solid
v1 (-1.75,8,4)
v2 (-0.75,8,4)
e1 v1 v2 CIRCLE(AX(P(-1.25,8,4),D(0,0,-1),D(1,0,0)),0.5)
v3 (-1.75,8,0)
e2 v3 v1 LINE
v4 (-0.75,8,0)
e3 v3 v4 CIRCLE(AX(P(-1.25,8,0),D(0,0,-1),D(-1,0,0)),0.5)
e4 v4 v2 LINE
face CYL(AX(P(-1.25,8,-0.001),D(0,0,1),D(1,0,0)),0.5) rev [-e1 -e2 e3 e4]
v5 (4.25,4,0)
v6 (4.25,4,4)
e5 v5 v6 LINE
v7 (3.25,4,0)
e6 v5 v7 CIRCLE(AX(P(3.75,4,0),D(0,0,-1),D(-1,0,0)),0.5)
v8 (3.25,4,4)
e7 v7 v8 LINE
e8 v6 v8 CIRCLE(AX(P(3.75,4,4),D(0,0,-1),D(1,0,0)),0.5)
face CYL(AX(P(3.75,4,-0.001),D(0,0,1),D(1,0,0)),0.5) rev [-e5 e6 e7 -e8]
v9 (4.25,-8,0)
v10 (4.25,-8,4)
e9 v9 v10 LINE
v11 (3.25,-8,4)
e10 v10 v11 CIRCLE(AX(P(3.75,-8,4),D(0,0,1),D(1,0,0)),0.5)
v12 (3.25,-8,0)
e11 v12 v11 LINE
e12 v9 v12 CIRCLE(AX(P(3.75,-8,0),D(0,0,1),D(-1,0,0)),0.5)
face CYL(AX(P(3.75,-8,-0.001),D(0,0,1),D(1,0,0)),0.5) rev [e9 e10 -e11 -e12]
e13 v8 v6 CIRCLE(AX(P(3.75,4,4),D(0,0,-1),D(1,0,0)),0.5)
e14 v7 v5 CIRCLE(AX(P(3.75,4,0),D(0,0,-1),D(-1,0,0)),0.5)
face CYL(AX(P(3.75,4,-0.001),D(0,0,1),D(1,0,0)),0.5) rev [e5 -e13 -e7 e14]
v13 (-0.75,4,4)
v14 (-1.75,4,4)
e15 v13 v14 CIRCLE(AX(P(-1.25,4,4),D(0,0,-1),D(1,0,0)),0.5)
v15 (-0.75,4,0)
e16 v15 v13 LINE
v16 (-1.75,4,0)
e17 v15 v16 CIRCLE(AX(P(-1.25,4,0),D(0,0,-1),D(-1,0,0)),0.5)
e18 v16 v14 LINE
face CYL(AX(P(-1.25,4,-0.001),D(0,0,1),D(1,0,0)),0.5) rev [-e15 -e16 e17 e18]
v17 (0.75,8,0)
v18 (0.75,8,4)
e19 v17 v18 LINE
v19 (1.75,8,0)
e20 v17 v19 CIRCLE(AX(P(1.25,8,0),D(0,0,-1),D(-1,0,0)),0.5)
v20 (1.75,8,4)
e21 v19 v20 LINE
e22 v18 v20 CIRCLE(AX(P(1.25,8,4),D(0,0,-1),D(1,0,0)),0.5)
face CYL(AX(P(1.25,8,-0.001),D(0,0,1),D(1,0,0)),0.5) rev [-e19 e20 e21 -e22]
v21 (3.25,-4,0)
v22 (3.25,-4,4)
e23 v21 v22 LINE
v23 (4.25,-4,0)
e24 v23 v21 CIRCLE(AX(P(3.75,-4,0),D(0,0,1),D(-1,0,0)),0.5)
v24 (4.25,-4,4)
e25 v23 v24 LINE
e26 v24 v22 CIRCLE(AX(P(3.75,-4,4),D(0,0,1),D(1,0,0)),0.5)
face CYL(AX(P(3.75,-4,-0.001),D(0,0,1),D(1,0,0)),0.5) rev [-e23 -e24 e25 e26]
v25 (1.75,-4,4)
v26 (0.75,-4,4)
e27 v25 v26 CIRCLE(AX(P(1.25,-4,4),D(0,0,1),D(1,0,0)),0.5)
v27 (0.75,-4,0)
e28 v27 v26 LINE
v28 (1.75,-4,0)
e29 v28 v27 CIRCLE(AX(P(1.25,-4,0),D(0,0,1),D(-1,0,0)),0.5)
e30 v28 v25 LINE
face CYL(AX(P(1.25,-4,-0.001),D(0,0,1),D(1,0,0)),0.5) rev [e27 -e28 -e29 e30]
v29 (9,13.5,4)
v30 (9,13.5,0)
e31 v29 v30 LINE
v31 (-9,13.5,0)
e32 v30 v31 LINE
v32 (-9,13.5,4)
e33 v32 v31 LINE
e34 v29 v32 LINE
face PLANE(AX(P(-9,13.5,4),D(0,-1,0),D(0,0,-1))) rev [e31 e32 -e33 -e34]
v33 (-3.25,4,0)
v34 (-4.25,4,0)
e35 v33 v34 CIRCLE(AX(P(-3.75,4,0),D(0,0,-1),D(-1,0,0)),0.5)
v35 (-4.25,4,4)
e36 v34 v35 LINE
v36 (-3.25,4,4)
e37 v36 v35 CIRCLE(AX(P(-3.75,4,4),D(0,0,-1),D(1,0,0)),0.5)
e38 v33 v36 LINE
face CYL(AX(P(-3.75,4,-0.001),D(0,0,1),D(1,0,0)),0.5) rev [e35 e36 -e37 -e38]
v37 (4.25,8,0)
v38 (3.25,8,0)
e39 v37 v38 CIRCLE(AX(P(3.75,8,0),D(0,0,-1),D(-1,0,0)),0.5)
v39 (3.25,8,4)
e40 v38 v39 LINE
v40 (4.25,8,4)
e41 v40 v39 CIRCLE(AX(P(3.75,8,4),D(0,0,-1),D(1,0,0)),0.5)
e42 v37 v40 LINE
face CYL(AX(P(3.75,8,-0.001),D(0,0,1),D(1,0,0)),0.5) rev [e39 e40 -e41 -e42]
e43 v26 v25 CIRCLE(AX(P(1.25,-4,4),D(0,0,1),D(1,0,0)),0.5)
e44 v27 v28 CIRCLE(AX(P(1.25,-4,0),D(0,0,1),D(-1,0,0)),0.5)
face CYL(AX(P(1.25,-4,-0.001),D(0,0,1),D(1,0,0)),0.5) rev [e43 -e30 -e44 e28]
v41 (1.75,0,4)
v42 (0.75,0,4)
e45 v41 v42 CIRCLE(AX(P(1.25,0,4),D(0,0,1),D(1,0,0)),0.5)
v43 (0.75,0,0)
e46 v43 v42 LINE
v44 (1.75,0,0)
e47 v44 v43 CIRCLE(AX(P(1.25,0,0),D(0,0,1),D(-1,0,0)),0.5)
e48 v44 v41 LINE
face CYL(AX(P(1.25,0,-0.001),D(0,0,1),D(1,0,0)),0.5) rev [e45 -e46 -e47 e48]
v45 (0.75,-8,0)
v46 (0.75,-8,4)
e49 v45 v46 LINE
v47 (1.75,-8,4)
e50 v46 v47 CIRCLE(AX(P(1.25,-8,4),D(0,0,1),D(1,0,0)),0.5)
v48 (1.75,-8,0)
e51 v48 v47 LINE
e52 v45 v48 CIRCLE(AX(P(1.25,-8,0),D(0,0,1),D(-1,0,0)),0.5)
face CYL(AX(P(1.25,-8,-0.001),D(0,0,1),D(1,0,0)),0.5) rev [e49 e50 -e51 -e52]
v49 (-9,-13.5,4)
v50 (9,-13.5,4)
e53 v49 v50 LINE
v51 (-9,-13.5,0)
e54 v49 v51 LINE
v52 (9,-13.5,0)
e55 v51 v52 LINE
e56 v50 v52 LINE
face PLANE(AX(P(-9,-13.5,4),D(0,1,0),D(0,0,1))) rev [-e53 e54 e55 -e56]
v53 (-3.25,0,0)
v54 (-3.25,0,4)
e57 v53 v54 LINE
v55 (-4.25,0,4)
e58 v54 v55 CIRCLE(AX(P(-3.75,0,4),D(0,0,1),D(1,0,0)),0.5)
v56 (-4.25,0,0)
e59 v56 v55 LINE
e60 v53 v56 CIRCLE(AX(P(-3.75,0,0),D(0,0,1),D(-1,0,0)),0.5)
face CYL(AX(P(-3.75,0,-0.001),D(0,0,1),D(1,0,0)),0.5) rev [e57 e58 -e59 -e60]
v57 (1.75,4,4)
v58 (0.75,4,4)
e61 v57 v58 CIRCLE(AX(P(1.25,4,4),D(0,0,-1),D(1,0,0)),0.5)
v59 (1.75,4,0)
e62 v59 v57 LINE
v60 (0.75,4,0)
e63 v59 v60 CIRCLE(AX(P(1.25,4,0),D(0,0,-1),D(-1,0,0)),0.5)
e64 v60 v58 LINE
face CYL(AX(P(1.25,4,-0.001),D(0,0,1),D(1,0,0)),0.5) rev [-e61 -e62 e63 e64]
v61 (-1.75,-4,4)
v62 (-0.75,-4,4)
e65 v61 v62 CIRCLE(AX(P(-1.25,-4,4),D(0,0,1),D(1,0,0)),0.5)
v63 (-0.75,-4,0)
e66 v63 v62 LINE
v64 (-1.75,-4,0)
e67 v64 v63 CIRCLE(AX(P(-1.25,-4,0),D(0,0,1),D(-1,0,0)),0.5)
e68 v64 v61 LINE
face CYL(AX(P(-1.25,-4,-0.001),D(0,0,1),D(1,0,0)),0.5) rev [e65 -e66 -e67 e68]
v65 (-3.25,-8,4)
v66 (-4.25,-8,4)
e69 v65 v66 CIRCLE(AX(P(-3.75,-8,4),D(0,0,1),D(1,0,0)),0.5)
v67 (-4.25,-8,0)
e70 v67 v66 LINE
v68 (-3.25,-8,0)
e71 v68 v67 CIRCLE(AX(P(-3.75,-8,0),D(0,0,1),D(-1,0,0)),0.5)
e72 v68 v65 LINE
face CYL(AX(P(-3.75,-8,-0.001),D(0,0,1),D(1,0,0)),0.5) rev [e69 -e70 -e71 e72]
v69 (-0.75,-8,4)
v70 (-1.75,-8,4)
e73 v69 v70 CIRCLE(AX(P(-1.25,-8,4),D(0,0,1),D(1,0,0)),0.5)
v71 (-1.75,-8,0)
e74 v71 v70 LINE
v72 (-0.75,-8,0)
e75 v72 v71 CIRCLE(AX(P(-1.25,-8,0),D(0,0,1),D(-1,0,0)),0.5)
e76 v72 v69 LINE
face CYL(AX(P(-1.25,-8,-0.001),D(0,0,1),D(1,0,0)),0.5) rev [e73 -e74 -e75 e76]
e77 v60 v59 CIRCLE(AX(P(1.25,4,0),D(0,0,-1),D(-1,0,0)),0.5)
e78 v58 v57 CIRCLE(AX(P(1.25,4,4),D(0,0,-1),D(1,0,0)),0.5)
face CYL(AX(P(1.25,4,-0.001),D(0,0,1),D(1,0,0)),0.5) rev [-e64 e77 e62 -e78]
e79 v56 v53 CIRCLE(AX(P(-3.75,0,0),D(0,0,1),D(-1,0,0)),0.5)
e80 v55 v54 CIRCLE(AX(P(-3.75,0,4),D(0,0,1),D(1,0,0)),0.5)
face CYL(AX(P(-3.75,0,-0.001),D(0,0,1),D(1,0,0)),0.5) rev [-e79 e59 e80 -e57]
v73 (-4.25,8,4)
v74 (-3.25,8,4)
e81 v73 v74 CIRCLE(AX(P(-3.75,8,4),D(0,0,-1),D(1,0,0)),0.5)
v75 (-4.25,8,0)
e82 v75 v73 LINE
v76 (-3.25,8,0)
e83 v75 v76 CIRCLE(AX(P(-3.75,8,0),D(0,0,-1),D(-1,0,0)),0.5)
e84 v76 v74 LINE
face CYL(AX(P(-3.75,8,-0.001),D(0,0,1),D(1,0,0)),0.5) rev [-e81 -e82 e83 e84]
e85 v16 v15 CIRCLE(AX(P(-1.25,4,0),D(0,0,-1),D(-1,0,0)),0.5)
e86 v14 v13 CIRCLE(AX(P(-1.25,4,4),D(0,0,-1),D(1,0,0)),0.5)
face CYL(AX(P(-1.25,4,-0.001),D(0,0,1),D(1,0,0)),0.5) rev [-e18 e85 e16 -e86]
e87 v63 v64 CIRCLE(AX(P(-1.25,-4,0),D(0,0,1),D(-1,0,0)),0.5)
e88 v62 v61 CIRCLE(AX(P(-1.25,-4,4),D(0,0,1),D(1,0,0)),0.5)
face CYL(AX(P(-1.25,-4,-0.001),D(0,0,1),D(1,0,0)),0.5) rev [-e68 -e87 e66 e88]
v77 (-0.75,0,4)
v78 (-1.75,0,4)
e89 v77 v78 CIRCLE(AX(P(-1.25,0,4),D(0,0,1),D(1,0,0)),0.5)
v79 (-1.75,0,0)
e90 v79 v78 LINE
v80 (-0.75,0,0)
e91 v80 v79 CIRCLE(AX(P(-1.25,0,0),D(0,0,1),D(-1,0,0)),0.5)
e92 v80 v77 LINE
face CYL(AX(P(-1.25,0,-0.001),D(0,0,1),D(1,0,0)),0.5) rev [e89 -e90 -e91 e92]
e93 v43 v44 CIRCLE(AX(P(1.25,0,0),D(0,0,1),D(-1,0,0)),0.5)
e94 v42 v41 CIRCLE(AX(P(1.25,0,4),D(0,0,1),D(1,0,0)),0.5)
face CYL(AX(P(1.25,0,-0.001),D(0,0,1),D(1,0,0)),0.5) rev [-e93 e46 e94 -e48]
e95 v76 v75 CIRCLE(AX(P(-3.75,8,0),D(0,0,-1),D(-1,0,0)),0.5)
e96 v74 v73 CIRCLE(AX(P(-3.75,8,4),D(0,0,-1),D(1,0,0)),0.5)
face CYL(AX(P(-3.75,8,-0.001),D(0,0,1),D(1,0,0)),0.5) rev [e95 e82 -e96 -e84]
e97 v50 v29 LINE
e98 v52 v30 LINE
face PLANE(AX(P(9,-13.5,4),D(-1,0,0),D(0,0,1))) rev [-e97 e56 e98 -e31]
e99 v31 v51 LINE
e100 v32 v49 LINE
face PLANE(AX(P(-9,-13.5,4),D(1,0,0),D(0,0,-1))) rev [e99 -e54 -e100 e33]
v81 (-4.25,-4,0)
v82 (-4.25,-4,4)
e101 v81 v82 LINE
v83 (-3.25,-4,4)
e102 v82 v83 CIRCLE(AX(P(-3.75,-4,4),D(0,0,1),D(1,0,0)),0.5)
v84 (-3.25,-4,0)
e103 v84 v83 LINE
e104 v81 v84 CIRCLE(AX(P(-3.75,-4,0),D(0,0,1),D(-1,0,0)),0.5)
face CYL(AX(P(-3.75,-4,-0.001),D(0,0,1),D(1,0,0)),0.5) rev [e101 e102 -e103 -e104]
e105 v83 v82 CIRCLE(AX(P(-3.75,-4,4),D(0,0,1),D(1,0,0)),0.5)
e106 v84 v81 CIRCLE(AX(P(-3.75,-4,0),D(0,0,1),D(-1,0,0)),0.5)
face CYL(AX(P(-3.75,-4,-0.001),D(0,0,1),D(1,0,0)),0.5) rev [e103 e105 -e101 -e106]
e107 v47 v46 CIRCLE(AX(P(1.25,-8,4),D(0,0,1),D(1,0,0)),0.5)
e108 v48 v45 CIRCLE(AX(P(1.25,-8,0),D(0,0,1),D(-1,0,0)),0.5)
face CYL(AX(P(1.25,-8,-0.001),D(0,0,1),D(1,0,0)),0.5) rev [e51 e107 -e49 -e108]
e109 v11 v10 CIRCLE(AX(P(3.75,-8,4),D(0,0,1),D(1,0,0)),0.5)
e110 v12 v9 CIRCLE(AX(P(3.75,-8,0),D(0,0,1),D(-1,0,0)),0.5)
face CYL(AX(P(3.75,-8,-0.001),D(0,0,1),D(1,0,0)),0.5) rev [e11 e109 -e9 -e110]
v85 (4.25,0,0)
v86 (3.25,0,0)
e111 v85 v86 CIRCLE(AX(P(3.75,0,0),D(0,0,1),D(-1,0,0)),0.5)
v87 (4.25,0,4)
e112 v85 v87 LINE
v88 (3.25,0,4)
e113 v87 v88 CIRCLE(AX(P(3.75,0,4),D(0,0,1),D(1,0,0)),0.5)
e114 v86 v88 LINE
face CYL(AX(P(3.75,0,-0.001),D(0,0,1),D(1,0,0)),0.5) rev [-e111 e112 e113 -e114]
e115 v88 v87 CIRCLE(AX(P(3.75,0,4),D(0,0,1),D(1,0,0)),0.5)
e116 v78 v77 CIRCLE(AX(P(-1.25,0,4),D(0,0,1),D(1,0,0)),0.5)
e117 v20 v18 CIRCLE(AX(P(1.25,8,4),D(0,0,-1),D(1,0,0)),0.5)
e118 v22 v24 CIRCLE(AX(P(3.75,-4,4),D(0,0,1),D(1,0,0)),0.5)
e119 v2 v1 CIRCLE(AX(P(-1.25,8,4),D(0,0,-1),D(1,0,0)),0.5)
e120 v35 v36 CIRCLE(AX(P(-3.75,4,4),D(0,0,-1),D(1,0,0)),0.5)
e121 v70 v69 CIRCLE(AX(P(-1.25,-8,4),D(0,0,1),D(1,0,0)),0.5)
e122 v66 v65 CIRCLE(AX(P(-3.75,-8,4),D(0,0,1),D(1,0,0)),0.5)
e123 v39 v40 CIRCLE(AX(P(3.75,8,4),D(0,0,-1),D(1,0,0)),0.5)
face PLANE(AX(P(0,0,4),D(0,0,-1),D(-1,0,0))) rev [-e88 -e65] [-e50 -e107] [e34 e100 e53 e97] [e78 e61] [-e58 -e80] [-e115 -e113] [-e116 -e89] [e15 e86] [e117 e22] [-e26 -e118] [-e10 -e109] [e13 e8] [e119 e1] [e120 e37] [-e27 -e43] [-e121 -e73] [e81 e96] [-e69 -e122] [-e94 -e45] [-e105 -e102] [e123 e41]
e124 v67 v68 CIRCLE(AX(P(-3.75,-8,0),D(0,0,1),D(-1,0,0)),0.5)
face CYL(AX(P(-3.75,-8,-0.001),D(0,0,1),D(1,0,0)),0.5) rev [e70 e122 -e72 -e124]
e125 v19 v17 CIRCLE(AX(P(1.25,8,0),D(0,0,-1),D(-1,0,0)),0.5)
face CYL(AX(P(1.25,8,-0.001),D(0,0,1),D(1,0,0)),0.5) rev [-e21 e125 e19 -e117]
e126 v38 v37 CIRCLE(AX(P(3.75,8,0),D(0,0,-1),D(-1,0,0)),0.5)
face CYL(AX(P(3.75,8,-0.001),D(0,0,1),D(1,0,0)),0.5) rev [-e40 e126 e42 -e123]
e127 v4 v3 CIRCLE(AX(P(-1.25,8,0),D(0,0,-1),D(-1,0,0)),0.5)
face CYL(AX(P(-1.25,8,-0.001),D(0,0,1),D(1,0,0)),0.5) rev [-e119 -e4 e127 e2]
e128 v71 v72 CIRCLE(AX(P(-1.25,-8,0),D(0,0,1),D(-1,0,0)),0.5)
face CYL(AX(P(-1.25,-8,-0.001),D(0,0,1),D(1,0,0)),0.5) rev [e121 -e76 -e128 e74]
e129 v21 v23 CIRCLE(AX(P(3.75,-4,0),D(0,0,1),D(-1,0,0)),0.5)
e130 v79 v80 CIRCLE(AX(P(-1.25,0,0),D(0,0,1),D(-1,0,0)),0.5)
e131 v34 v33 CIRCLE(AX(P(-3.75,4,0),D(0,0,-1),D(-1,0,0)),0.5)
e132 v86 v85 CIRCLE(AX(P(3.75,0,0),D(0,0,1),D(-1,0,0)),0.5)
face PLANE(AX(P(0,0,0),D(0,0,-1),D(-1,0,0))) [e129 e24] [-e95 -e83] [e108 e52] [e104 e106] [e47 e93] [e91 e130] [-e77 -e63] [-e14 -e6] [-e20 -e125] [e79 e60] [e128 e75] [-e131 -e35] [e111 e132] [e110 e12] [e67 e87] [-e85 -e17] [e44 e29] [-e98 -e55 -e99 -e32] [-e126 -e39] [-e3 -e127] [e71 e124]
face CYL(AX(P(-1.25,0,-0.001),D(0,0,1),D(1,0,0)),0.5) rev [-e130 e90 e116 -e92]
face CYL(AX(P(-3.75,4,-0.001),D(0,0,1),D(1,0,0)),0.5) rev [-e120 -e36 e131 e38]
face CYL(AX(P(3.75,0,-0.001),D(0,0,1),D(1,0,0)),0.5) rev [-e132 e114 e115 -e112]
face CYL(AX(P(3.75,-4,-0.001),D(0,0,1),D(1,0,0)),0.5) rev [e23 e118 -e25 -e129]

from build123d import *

# Parameters (mm, degrees)
SKETCH_1_W               = 18
SKETCH_1_H               = 27
EXTRUDE_1_DEPTH          = 4
CUT_EXTRUDE_1_REACH      = 18.711
SKETCH_2_R               = 0.5
PATTERN_LINEAR_2_COUNT   = 3
PATTERN_LINEAR_2_PITCH   = 4
MIRROR_1_COPY_1_REACH    = 18.711
MIRROR_1_COPY_1_SKETCH_R = 0.5
MIRROR_1_COPY_2_REACH    = 18.711
MIRROR_1_COPY_2_SKETCH_R = 0.5


with BuildPart() as part:
    # 草图1 → 凸台-拉伸1 (new body)
    with BuildSketch(Plane.XY):
        Rectangle(SKETCH_1_W, SKETCH_1_H)
    extrude(amount=EXTRUDE_1_DEPTH)

    # 草图2 → 切除-拉伸1 (cut, up to next)
    with BuildSketch(Plane.XY.offset(4), mode=Mode.PRIVATE) as cut_extrude_1_sk1:
        with Locations((-1.25, 0)):
            Circle(SKETCH_2_R)
    cut_extrude_1_tool1 = extrude(cut_extrude_1_sk1.sketch, amount=-CUT_EXTRUDE_1_REACH, mode=Mode.PRIVATE) & part.part
    # 草图2 → 切除-拉伸1 (cut, up to next)
    with BuildSketch(Plane.XY.offset(4), mode=Mode.PRIVATE) as cut_extrude_1_sk2:
        with Locations((-3.75, 0)):
            Circle(SKETCH_2_R)
    cut_extrude_1_tool2 = extrude(cut_extrude_1_sk2.sketch, amount=-CUT_EXTRUDE_1_REACH, mode=Mode.PRIVATE) & part.part
    # 草图2 → 切除-拉伸1 (cut, up to next)
    with BuildSketch(Plane.XY.offset(4), mode=Mode.PRIVATE) as cut_extrude_1_sk3:
        with Locations((1.25, 0)):
            Circle(SKETCH_2_R)
    cut_extrude_1_tool3 = extrude(cut_extrude_1_sk3.sketch, amount=-CUT_EXTRUDE_1_REACH, mode=Mode.PRIVATE) & part.part
    # 草图2 → 切除-拉伸1 (cut, up to next)
    with BuildSketch(Plane.XY.offset(4), mode=Mode.PRIVATE) as cut_extrude_1_sk4:
        with Locations((3.75, 0)):
            Circle(SKETCH_2_R)
    cut_extrude_1_tool4 = extrude(cut_extrude_1_sk4.sketch, amount=-CUT_EXTRUDE_1_REACH, mode=Mode.PRIVATE) & part.part
    cut_extrude_1_1 = cut_extrude_1_tool1.solids().sort_by_distance((-1.25, 0, 4))[0]
    add(cut_extrude_1_1, mode=Mode.SUBTRACT)
    cut_extrude_1_2 = cut_extrude_1_tool2.solids().sort_by_distance((-3.75, 0, 4))[0]
    add(cut_extrude_1_2, mode=Mode.SUBTRACT)
    cut_extrude_1_3 = cut_extrude_1_tool3.solids().sort_by_distance((1.25, 0, 4))[0]
    add(cut_extrude_1_3, mode=Mode.SUBTRACT)
    cut_extrude_1_4 = cut_extrude_1_tool4.solids().sort_by_distance((3.75, 0, 4))[0]
    add(cut_extrude_1_4, mode=Mode.SUBTRACT)
    cut_extrude_1 = cut_extrude_1_1 + cut_extrude_1_2 + cut_extrude_1_3 + cut_extrude_1_4  # 切除-拉伸1 as one shape, for the pattern or mirror that repeats it

    # 阵列(线性)2: 切除-拉伸1 ×3
    with Locations(*[(0, -i * PATTERN_LINEAR_2_PITCH, 0) for i in range(1, PATTERN_LINEAR_2_COUNT)]):
        add(cut_extrude_1, mode=Mode.SUBTRACT)

    # 镜向1 copy 1 sketch → 镜向1 copy 1 (cut, up to next)
    with BuildSketch(Plane(origin=(0, 4, 4), x_dir=(1, 0, 0), z_dir=(0, 0, 1)), mode=Mode.PRIVATE) as mirror_1_copy_1_sk1:
        with Locations((-1.25, 0)):
            Circle(MIRROR_1_COPY_1_SKETCH_R)
    mirror_1_copy_1_tool1 = extrude(mirror_1_copy_1_sk1.sketch, amount=-MIRROR_1_COPY_1_REACH, mode=Mode.PRIVATE) & part.part
    # 镜向1 copy 1 sketch → 镜向1 copy 1 (cut, up to next)
    with BuildSketch(Plane(origin=(0, 4, 4), x_dir=(1, 0, 0), z_dir=(0, 0, 1)), mode=Mode.PRIVATE) as mirror_1_copy_1_sk2:
        with Locations((-3.75, 0)):
            Circle(MIRROR_1_COPY_1_SKETCH_R)
    mirror_1_copy_1_tool2 = extrude(mirror_1_copy_1_sk2.sketch, amount=-MIRROR_1_COPY_1_REACH, mode=Mode.PRIVATE) & part.part
    # 镜向1 copy 1 sketch → 镜向1 copy 1 (cut, up to next)
    with BuildSketch(Plane(origin=(0, 4, 4), x_dir=(1, 0, 0), z_dir=(0, 0, 1)), mode=Mode.PRIVATE) as mirror_1_copy_1_sk3:
        with Locations((1.25, 0)):
            Circle(MIRROR_1_COPY_1_SKETCH_R)
    mirror_1_copy_1_tool3 = extrude(mirror_1_copy_1_sk3.sketch, amount=-MIRROR_1_COPY_1_REACH, mode=Mode.PRIVATE) & part.part
    # 镜向1 copy 1 sketch → 镜向1 copy 1 (cut, up to next)
    with BuildSketch(Plane(origin=(0, 4, 4), x_dir=(1, 0, 0), z_dir=(0, 0, 1)), mode=Mode.PRIVATE) as mirror_1_copy_1_sk4:
        with Locations((3.75, 0)):
            Circle(MIRROR_1_COPY_1_SKETCH_R)
    mirror_1_copy_1_tool4 = extrude(mirror_1_copy_1_sk4.sketch, amount=-MIRROR_1_COPY_1_REACH, mode=Mode.PRIVATE) & part.part
    add(mirror_1_copy_1_tool1.solids().sort_by_distance((-1.25, 4, 4))[0], mode=Mode.SUBTRACT)
    add(mirror_1_copy_1_tool2.solids().sort_by_distance((-3.75, 4, 4))[0], mode=Mode.SUBTRACT)
    add(mirror_1_copy_1_tool3.solids().sort_by_distance((1.25, 4, 4))[0], mode=Mode.SUBTRACT)
    add(mirror_1_copy_1_tool4.solids().sort_by_distance((3.75, 4, 4))[0], mode=Mode.SUBTRACT)

    # 镜向1 copy 2 sketch → 镜向1 copy 2 (cut, up to next)
    with BuildSketch(Plane(origin=(0, 8, 4), x_dir=(1, 0, 0), z_dir=(0, 0, 1)), mode=Mode.PRIVATE) as mirror_1_copy_2_sk1:
        with Locations((-1.25, 0)):
            Circle(MIRROR_1_COPY_2_SKETCH_R)
    mirror_1_copy_2_tool1 = extrude(mirror_1_copy_2_sk1.sketch, amount=-MIRROR_1_COPY_2_REACH, mode=Mode.PRIVATE) & part.part
    # 镜向1 copy 2 sketch → 镜向1 copy 2 (cut, up to next)
    with BuildSketch(Plane(origin=(0, 8, 4), x_dir=(1, 0, 0), z_dir=(0, 0, 1)), mode=Mode.PRIVATE) as mirror_1_copy_2_sk2:
        with Locations((-3.75, 0)):
            Circle(MIRROR_1_COPY_2_SKETCH_R)
    mirror_1_copy_2_tool2 = extrude(mirror_1_copy_2_sk2.sketch, amount=-MIRROR_1_COPY_2_REACH, mode=Mode.PRIVATE) & part.part
    # 镜向1 copy 2 sketch → 镜向1 copy 2 (cut, up to next)
    with BuildSketch(Plane(origin=(0, 8, 4), x_dir=(1, 0, 0), z_dir=(0, 0, 1)), mode=Mode.PRIVATE) as mirror_1_copy_2_sk3:
        with Locations((1.25, 0)):
            Circle(MIRROR_1_COPY_2_SKETCH_R)
    mirror_1_copy_2_tool3 = extrude(mirror_1_copy_2_sk3.sketch, amount=-MIRROR_1_COPY_2_REACH, mode=Mode.PRIVATE) & part.part
    # 镜向1 copy 2 sketch → 镜向1 copy 2 (cut, up to next)
    with BuildSketch(Plane(origin=(0, 8, 4), x_dir=(1, 0, 0), z_dir=(0, 0, 1)), mode=Mode.PRIVATE) as mirror_1_copy_2_sk4:
        with Locations((3.75, 0)):
            Circle(MIRROR_1_COPY_2_SKETCH_R)
    mirror_1_copy_2_tool4 = extrude(mirror_1_copy_2_sk4.sketch, amount=-MIRROR_1_COPY_2_REACH, mode=Mode.PRIVATE) & part.part
    add(mirror_1_copy_2_tool1.solids().sort_by_distance((-1.25, 8, 4))[0], mode=Mode.SUBTRACT)
    add(mirror_1_copy_2_tool2.solids().sort_by_distance((-3.75, 8, 4))[0], mode=Mode.SUBTRACT)
    add(mirror_1_copy_2_tool3.solids().sort_by_distance((1.25, 8, 4))[0], mode=Mode.SUBTRACT)
    add(mirror_1_copy_2_tool4.solids().sort_by_distance((3.75, 8, 4))[0], mode=Mode.SUBTRACT)


solid = part.part
